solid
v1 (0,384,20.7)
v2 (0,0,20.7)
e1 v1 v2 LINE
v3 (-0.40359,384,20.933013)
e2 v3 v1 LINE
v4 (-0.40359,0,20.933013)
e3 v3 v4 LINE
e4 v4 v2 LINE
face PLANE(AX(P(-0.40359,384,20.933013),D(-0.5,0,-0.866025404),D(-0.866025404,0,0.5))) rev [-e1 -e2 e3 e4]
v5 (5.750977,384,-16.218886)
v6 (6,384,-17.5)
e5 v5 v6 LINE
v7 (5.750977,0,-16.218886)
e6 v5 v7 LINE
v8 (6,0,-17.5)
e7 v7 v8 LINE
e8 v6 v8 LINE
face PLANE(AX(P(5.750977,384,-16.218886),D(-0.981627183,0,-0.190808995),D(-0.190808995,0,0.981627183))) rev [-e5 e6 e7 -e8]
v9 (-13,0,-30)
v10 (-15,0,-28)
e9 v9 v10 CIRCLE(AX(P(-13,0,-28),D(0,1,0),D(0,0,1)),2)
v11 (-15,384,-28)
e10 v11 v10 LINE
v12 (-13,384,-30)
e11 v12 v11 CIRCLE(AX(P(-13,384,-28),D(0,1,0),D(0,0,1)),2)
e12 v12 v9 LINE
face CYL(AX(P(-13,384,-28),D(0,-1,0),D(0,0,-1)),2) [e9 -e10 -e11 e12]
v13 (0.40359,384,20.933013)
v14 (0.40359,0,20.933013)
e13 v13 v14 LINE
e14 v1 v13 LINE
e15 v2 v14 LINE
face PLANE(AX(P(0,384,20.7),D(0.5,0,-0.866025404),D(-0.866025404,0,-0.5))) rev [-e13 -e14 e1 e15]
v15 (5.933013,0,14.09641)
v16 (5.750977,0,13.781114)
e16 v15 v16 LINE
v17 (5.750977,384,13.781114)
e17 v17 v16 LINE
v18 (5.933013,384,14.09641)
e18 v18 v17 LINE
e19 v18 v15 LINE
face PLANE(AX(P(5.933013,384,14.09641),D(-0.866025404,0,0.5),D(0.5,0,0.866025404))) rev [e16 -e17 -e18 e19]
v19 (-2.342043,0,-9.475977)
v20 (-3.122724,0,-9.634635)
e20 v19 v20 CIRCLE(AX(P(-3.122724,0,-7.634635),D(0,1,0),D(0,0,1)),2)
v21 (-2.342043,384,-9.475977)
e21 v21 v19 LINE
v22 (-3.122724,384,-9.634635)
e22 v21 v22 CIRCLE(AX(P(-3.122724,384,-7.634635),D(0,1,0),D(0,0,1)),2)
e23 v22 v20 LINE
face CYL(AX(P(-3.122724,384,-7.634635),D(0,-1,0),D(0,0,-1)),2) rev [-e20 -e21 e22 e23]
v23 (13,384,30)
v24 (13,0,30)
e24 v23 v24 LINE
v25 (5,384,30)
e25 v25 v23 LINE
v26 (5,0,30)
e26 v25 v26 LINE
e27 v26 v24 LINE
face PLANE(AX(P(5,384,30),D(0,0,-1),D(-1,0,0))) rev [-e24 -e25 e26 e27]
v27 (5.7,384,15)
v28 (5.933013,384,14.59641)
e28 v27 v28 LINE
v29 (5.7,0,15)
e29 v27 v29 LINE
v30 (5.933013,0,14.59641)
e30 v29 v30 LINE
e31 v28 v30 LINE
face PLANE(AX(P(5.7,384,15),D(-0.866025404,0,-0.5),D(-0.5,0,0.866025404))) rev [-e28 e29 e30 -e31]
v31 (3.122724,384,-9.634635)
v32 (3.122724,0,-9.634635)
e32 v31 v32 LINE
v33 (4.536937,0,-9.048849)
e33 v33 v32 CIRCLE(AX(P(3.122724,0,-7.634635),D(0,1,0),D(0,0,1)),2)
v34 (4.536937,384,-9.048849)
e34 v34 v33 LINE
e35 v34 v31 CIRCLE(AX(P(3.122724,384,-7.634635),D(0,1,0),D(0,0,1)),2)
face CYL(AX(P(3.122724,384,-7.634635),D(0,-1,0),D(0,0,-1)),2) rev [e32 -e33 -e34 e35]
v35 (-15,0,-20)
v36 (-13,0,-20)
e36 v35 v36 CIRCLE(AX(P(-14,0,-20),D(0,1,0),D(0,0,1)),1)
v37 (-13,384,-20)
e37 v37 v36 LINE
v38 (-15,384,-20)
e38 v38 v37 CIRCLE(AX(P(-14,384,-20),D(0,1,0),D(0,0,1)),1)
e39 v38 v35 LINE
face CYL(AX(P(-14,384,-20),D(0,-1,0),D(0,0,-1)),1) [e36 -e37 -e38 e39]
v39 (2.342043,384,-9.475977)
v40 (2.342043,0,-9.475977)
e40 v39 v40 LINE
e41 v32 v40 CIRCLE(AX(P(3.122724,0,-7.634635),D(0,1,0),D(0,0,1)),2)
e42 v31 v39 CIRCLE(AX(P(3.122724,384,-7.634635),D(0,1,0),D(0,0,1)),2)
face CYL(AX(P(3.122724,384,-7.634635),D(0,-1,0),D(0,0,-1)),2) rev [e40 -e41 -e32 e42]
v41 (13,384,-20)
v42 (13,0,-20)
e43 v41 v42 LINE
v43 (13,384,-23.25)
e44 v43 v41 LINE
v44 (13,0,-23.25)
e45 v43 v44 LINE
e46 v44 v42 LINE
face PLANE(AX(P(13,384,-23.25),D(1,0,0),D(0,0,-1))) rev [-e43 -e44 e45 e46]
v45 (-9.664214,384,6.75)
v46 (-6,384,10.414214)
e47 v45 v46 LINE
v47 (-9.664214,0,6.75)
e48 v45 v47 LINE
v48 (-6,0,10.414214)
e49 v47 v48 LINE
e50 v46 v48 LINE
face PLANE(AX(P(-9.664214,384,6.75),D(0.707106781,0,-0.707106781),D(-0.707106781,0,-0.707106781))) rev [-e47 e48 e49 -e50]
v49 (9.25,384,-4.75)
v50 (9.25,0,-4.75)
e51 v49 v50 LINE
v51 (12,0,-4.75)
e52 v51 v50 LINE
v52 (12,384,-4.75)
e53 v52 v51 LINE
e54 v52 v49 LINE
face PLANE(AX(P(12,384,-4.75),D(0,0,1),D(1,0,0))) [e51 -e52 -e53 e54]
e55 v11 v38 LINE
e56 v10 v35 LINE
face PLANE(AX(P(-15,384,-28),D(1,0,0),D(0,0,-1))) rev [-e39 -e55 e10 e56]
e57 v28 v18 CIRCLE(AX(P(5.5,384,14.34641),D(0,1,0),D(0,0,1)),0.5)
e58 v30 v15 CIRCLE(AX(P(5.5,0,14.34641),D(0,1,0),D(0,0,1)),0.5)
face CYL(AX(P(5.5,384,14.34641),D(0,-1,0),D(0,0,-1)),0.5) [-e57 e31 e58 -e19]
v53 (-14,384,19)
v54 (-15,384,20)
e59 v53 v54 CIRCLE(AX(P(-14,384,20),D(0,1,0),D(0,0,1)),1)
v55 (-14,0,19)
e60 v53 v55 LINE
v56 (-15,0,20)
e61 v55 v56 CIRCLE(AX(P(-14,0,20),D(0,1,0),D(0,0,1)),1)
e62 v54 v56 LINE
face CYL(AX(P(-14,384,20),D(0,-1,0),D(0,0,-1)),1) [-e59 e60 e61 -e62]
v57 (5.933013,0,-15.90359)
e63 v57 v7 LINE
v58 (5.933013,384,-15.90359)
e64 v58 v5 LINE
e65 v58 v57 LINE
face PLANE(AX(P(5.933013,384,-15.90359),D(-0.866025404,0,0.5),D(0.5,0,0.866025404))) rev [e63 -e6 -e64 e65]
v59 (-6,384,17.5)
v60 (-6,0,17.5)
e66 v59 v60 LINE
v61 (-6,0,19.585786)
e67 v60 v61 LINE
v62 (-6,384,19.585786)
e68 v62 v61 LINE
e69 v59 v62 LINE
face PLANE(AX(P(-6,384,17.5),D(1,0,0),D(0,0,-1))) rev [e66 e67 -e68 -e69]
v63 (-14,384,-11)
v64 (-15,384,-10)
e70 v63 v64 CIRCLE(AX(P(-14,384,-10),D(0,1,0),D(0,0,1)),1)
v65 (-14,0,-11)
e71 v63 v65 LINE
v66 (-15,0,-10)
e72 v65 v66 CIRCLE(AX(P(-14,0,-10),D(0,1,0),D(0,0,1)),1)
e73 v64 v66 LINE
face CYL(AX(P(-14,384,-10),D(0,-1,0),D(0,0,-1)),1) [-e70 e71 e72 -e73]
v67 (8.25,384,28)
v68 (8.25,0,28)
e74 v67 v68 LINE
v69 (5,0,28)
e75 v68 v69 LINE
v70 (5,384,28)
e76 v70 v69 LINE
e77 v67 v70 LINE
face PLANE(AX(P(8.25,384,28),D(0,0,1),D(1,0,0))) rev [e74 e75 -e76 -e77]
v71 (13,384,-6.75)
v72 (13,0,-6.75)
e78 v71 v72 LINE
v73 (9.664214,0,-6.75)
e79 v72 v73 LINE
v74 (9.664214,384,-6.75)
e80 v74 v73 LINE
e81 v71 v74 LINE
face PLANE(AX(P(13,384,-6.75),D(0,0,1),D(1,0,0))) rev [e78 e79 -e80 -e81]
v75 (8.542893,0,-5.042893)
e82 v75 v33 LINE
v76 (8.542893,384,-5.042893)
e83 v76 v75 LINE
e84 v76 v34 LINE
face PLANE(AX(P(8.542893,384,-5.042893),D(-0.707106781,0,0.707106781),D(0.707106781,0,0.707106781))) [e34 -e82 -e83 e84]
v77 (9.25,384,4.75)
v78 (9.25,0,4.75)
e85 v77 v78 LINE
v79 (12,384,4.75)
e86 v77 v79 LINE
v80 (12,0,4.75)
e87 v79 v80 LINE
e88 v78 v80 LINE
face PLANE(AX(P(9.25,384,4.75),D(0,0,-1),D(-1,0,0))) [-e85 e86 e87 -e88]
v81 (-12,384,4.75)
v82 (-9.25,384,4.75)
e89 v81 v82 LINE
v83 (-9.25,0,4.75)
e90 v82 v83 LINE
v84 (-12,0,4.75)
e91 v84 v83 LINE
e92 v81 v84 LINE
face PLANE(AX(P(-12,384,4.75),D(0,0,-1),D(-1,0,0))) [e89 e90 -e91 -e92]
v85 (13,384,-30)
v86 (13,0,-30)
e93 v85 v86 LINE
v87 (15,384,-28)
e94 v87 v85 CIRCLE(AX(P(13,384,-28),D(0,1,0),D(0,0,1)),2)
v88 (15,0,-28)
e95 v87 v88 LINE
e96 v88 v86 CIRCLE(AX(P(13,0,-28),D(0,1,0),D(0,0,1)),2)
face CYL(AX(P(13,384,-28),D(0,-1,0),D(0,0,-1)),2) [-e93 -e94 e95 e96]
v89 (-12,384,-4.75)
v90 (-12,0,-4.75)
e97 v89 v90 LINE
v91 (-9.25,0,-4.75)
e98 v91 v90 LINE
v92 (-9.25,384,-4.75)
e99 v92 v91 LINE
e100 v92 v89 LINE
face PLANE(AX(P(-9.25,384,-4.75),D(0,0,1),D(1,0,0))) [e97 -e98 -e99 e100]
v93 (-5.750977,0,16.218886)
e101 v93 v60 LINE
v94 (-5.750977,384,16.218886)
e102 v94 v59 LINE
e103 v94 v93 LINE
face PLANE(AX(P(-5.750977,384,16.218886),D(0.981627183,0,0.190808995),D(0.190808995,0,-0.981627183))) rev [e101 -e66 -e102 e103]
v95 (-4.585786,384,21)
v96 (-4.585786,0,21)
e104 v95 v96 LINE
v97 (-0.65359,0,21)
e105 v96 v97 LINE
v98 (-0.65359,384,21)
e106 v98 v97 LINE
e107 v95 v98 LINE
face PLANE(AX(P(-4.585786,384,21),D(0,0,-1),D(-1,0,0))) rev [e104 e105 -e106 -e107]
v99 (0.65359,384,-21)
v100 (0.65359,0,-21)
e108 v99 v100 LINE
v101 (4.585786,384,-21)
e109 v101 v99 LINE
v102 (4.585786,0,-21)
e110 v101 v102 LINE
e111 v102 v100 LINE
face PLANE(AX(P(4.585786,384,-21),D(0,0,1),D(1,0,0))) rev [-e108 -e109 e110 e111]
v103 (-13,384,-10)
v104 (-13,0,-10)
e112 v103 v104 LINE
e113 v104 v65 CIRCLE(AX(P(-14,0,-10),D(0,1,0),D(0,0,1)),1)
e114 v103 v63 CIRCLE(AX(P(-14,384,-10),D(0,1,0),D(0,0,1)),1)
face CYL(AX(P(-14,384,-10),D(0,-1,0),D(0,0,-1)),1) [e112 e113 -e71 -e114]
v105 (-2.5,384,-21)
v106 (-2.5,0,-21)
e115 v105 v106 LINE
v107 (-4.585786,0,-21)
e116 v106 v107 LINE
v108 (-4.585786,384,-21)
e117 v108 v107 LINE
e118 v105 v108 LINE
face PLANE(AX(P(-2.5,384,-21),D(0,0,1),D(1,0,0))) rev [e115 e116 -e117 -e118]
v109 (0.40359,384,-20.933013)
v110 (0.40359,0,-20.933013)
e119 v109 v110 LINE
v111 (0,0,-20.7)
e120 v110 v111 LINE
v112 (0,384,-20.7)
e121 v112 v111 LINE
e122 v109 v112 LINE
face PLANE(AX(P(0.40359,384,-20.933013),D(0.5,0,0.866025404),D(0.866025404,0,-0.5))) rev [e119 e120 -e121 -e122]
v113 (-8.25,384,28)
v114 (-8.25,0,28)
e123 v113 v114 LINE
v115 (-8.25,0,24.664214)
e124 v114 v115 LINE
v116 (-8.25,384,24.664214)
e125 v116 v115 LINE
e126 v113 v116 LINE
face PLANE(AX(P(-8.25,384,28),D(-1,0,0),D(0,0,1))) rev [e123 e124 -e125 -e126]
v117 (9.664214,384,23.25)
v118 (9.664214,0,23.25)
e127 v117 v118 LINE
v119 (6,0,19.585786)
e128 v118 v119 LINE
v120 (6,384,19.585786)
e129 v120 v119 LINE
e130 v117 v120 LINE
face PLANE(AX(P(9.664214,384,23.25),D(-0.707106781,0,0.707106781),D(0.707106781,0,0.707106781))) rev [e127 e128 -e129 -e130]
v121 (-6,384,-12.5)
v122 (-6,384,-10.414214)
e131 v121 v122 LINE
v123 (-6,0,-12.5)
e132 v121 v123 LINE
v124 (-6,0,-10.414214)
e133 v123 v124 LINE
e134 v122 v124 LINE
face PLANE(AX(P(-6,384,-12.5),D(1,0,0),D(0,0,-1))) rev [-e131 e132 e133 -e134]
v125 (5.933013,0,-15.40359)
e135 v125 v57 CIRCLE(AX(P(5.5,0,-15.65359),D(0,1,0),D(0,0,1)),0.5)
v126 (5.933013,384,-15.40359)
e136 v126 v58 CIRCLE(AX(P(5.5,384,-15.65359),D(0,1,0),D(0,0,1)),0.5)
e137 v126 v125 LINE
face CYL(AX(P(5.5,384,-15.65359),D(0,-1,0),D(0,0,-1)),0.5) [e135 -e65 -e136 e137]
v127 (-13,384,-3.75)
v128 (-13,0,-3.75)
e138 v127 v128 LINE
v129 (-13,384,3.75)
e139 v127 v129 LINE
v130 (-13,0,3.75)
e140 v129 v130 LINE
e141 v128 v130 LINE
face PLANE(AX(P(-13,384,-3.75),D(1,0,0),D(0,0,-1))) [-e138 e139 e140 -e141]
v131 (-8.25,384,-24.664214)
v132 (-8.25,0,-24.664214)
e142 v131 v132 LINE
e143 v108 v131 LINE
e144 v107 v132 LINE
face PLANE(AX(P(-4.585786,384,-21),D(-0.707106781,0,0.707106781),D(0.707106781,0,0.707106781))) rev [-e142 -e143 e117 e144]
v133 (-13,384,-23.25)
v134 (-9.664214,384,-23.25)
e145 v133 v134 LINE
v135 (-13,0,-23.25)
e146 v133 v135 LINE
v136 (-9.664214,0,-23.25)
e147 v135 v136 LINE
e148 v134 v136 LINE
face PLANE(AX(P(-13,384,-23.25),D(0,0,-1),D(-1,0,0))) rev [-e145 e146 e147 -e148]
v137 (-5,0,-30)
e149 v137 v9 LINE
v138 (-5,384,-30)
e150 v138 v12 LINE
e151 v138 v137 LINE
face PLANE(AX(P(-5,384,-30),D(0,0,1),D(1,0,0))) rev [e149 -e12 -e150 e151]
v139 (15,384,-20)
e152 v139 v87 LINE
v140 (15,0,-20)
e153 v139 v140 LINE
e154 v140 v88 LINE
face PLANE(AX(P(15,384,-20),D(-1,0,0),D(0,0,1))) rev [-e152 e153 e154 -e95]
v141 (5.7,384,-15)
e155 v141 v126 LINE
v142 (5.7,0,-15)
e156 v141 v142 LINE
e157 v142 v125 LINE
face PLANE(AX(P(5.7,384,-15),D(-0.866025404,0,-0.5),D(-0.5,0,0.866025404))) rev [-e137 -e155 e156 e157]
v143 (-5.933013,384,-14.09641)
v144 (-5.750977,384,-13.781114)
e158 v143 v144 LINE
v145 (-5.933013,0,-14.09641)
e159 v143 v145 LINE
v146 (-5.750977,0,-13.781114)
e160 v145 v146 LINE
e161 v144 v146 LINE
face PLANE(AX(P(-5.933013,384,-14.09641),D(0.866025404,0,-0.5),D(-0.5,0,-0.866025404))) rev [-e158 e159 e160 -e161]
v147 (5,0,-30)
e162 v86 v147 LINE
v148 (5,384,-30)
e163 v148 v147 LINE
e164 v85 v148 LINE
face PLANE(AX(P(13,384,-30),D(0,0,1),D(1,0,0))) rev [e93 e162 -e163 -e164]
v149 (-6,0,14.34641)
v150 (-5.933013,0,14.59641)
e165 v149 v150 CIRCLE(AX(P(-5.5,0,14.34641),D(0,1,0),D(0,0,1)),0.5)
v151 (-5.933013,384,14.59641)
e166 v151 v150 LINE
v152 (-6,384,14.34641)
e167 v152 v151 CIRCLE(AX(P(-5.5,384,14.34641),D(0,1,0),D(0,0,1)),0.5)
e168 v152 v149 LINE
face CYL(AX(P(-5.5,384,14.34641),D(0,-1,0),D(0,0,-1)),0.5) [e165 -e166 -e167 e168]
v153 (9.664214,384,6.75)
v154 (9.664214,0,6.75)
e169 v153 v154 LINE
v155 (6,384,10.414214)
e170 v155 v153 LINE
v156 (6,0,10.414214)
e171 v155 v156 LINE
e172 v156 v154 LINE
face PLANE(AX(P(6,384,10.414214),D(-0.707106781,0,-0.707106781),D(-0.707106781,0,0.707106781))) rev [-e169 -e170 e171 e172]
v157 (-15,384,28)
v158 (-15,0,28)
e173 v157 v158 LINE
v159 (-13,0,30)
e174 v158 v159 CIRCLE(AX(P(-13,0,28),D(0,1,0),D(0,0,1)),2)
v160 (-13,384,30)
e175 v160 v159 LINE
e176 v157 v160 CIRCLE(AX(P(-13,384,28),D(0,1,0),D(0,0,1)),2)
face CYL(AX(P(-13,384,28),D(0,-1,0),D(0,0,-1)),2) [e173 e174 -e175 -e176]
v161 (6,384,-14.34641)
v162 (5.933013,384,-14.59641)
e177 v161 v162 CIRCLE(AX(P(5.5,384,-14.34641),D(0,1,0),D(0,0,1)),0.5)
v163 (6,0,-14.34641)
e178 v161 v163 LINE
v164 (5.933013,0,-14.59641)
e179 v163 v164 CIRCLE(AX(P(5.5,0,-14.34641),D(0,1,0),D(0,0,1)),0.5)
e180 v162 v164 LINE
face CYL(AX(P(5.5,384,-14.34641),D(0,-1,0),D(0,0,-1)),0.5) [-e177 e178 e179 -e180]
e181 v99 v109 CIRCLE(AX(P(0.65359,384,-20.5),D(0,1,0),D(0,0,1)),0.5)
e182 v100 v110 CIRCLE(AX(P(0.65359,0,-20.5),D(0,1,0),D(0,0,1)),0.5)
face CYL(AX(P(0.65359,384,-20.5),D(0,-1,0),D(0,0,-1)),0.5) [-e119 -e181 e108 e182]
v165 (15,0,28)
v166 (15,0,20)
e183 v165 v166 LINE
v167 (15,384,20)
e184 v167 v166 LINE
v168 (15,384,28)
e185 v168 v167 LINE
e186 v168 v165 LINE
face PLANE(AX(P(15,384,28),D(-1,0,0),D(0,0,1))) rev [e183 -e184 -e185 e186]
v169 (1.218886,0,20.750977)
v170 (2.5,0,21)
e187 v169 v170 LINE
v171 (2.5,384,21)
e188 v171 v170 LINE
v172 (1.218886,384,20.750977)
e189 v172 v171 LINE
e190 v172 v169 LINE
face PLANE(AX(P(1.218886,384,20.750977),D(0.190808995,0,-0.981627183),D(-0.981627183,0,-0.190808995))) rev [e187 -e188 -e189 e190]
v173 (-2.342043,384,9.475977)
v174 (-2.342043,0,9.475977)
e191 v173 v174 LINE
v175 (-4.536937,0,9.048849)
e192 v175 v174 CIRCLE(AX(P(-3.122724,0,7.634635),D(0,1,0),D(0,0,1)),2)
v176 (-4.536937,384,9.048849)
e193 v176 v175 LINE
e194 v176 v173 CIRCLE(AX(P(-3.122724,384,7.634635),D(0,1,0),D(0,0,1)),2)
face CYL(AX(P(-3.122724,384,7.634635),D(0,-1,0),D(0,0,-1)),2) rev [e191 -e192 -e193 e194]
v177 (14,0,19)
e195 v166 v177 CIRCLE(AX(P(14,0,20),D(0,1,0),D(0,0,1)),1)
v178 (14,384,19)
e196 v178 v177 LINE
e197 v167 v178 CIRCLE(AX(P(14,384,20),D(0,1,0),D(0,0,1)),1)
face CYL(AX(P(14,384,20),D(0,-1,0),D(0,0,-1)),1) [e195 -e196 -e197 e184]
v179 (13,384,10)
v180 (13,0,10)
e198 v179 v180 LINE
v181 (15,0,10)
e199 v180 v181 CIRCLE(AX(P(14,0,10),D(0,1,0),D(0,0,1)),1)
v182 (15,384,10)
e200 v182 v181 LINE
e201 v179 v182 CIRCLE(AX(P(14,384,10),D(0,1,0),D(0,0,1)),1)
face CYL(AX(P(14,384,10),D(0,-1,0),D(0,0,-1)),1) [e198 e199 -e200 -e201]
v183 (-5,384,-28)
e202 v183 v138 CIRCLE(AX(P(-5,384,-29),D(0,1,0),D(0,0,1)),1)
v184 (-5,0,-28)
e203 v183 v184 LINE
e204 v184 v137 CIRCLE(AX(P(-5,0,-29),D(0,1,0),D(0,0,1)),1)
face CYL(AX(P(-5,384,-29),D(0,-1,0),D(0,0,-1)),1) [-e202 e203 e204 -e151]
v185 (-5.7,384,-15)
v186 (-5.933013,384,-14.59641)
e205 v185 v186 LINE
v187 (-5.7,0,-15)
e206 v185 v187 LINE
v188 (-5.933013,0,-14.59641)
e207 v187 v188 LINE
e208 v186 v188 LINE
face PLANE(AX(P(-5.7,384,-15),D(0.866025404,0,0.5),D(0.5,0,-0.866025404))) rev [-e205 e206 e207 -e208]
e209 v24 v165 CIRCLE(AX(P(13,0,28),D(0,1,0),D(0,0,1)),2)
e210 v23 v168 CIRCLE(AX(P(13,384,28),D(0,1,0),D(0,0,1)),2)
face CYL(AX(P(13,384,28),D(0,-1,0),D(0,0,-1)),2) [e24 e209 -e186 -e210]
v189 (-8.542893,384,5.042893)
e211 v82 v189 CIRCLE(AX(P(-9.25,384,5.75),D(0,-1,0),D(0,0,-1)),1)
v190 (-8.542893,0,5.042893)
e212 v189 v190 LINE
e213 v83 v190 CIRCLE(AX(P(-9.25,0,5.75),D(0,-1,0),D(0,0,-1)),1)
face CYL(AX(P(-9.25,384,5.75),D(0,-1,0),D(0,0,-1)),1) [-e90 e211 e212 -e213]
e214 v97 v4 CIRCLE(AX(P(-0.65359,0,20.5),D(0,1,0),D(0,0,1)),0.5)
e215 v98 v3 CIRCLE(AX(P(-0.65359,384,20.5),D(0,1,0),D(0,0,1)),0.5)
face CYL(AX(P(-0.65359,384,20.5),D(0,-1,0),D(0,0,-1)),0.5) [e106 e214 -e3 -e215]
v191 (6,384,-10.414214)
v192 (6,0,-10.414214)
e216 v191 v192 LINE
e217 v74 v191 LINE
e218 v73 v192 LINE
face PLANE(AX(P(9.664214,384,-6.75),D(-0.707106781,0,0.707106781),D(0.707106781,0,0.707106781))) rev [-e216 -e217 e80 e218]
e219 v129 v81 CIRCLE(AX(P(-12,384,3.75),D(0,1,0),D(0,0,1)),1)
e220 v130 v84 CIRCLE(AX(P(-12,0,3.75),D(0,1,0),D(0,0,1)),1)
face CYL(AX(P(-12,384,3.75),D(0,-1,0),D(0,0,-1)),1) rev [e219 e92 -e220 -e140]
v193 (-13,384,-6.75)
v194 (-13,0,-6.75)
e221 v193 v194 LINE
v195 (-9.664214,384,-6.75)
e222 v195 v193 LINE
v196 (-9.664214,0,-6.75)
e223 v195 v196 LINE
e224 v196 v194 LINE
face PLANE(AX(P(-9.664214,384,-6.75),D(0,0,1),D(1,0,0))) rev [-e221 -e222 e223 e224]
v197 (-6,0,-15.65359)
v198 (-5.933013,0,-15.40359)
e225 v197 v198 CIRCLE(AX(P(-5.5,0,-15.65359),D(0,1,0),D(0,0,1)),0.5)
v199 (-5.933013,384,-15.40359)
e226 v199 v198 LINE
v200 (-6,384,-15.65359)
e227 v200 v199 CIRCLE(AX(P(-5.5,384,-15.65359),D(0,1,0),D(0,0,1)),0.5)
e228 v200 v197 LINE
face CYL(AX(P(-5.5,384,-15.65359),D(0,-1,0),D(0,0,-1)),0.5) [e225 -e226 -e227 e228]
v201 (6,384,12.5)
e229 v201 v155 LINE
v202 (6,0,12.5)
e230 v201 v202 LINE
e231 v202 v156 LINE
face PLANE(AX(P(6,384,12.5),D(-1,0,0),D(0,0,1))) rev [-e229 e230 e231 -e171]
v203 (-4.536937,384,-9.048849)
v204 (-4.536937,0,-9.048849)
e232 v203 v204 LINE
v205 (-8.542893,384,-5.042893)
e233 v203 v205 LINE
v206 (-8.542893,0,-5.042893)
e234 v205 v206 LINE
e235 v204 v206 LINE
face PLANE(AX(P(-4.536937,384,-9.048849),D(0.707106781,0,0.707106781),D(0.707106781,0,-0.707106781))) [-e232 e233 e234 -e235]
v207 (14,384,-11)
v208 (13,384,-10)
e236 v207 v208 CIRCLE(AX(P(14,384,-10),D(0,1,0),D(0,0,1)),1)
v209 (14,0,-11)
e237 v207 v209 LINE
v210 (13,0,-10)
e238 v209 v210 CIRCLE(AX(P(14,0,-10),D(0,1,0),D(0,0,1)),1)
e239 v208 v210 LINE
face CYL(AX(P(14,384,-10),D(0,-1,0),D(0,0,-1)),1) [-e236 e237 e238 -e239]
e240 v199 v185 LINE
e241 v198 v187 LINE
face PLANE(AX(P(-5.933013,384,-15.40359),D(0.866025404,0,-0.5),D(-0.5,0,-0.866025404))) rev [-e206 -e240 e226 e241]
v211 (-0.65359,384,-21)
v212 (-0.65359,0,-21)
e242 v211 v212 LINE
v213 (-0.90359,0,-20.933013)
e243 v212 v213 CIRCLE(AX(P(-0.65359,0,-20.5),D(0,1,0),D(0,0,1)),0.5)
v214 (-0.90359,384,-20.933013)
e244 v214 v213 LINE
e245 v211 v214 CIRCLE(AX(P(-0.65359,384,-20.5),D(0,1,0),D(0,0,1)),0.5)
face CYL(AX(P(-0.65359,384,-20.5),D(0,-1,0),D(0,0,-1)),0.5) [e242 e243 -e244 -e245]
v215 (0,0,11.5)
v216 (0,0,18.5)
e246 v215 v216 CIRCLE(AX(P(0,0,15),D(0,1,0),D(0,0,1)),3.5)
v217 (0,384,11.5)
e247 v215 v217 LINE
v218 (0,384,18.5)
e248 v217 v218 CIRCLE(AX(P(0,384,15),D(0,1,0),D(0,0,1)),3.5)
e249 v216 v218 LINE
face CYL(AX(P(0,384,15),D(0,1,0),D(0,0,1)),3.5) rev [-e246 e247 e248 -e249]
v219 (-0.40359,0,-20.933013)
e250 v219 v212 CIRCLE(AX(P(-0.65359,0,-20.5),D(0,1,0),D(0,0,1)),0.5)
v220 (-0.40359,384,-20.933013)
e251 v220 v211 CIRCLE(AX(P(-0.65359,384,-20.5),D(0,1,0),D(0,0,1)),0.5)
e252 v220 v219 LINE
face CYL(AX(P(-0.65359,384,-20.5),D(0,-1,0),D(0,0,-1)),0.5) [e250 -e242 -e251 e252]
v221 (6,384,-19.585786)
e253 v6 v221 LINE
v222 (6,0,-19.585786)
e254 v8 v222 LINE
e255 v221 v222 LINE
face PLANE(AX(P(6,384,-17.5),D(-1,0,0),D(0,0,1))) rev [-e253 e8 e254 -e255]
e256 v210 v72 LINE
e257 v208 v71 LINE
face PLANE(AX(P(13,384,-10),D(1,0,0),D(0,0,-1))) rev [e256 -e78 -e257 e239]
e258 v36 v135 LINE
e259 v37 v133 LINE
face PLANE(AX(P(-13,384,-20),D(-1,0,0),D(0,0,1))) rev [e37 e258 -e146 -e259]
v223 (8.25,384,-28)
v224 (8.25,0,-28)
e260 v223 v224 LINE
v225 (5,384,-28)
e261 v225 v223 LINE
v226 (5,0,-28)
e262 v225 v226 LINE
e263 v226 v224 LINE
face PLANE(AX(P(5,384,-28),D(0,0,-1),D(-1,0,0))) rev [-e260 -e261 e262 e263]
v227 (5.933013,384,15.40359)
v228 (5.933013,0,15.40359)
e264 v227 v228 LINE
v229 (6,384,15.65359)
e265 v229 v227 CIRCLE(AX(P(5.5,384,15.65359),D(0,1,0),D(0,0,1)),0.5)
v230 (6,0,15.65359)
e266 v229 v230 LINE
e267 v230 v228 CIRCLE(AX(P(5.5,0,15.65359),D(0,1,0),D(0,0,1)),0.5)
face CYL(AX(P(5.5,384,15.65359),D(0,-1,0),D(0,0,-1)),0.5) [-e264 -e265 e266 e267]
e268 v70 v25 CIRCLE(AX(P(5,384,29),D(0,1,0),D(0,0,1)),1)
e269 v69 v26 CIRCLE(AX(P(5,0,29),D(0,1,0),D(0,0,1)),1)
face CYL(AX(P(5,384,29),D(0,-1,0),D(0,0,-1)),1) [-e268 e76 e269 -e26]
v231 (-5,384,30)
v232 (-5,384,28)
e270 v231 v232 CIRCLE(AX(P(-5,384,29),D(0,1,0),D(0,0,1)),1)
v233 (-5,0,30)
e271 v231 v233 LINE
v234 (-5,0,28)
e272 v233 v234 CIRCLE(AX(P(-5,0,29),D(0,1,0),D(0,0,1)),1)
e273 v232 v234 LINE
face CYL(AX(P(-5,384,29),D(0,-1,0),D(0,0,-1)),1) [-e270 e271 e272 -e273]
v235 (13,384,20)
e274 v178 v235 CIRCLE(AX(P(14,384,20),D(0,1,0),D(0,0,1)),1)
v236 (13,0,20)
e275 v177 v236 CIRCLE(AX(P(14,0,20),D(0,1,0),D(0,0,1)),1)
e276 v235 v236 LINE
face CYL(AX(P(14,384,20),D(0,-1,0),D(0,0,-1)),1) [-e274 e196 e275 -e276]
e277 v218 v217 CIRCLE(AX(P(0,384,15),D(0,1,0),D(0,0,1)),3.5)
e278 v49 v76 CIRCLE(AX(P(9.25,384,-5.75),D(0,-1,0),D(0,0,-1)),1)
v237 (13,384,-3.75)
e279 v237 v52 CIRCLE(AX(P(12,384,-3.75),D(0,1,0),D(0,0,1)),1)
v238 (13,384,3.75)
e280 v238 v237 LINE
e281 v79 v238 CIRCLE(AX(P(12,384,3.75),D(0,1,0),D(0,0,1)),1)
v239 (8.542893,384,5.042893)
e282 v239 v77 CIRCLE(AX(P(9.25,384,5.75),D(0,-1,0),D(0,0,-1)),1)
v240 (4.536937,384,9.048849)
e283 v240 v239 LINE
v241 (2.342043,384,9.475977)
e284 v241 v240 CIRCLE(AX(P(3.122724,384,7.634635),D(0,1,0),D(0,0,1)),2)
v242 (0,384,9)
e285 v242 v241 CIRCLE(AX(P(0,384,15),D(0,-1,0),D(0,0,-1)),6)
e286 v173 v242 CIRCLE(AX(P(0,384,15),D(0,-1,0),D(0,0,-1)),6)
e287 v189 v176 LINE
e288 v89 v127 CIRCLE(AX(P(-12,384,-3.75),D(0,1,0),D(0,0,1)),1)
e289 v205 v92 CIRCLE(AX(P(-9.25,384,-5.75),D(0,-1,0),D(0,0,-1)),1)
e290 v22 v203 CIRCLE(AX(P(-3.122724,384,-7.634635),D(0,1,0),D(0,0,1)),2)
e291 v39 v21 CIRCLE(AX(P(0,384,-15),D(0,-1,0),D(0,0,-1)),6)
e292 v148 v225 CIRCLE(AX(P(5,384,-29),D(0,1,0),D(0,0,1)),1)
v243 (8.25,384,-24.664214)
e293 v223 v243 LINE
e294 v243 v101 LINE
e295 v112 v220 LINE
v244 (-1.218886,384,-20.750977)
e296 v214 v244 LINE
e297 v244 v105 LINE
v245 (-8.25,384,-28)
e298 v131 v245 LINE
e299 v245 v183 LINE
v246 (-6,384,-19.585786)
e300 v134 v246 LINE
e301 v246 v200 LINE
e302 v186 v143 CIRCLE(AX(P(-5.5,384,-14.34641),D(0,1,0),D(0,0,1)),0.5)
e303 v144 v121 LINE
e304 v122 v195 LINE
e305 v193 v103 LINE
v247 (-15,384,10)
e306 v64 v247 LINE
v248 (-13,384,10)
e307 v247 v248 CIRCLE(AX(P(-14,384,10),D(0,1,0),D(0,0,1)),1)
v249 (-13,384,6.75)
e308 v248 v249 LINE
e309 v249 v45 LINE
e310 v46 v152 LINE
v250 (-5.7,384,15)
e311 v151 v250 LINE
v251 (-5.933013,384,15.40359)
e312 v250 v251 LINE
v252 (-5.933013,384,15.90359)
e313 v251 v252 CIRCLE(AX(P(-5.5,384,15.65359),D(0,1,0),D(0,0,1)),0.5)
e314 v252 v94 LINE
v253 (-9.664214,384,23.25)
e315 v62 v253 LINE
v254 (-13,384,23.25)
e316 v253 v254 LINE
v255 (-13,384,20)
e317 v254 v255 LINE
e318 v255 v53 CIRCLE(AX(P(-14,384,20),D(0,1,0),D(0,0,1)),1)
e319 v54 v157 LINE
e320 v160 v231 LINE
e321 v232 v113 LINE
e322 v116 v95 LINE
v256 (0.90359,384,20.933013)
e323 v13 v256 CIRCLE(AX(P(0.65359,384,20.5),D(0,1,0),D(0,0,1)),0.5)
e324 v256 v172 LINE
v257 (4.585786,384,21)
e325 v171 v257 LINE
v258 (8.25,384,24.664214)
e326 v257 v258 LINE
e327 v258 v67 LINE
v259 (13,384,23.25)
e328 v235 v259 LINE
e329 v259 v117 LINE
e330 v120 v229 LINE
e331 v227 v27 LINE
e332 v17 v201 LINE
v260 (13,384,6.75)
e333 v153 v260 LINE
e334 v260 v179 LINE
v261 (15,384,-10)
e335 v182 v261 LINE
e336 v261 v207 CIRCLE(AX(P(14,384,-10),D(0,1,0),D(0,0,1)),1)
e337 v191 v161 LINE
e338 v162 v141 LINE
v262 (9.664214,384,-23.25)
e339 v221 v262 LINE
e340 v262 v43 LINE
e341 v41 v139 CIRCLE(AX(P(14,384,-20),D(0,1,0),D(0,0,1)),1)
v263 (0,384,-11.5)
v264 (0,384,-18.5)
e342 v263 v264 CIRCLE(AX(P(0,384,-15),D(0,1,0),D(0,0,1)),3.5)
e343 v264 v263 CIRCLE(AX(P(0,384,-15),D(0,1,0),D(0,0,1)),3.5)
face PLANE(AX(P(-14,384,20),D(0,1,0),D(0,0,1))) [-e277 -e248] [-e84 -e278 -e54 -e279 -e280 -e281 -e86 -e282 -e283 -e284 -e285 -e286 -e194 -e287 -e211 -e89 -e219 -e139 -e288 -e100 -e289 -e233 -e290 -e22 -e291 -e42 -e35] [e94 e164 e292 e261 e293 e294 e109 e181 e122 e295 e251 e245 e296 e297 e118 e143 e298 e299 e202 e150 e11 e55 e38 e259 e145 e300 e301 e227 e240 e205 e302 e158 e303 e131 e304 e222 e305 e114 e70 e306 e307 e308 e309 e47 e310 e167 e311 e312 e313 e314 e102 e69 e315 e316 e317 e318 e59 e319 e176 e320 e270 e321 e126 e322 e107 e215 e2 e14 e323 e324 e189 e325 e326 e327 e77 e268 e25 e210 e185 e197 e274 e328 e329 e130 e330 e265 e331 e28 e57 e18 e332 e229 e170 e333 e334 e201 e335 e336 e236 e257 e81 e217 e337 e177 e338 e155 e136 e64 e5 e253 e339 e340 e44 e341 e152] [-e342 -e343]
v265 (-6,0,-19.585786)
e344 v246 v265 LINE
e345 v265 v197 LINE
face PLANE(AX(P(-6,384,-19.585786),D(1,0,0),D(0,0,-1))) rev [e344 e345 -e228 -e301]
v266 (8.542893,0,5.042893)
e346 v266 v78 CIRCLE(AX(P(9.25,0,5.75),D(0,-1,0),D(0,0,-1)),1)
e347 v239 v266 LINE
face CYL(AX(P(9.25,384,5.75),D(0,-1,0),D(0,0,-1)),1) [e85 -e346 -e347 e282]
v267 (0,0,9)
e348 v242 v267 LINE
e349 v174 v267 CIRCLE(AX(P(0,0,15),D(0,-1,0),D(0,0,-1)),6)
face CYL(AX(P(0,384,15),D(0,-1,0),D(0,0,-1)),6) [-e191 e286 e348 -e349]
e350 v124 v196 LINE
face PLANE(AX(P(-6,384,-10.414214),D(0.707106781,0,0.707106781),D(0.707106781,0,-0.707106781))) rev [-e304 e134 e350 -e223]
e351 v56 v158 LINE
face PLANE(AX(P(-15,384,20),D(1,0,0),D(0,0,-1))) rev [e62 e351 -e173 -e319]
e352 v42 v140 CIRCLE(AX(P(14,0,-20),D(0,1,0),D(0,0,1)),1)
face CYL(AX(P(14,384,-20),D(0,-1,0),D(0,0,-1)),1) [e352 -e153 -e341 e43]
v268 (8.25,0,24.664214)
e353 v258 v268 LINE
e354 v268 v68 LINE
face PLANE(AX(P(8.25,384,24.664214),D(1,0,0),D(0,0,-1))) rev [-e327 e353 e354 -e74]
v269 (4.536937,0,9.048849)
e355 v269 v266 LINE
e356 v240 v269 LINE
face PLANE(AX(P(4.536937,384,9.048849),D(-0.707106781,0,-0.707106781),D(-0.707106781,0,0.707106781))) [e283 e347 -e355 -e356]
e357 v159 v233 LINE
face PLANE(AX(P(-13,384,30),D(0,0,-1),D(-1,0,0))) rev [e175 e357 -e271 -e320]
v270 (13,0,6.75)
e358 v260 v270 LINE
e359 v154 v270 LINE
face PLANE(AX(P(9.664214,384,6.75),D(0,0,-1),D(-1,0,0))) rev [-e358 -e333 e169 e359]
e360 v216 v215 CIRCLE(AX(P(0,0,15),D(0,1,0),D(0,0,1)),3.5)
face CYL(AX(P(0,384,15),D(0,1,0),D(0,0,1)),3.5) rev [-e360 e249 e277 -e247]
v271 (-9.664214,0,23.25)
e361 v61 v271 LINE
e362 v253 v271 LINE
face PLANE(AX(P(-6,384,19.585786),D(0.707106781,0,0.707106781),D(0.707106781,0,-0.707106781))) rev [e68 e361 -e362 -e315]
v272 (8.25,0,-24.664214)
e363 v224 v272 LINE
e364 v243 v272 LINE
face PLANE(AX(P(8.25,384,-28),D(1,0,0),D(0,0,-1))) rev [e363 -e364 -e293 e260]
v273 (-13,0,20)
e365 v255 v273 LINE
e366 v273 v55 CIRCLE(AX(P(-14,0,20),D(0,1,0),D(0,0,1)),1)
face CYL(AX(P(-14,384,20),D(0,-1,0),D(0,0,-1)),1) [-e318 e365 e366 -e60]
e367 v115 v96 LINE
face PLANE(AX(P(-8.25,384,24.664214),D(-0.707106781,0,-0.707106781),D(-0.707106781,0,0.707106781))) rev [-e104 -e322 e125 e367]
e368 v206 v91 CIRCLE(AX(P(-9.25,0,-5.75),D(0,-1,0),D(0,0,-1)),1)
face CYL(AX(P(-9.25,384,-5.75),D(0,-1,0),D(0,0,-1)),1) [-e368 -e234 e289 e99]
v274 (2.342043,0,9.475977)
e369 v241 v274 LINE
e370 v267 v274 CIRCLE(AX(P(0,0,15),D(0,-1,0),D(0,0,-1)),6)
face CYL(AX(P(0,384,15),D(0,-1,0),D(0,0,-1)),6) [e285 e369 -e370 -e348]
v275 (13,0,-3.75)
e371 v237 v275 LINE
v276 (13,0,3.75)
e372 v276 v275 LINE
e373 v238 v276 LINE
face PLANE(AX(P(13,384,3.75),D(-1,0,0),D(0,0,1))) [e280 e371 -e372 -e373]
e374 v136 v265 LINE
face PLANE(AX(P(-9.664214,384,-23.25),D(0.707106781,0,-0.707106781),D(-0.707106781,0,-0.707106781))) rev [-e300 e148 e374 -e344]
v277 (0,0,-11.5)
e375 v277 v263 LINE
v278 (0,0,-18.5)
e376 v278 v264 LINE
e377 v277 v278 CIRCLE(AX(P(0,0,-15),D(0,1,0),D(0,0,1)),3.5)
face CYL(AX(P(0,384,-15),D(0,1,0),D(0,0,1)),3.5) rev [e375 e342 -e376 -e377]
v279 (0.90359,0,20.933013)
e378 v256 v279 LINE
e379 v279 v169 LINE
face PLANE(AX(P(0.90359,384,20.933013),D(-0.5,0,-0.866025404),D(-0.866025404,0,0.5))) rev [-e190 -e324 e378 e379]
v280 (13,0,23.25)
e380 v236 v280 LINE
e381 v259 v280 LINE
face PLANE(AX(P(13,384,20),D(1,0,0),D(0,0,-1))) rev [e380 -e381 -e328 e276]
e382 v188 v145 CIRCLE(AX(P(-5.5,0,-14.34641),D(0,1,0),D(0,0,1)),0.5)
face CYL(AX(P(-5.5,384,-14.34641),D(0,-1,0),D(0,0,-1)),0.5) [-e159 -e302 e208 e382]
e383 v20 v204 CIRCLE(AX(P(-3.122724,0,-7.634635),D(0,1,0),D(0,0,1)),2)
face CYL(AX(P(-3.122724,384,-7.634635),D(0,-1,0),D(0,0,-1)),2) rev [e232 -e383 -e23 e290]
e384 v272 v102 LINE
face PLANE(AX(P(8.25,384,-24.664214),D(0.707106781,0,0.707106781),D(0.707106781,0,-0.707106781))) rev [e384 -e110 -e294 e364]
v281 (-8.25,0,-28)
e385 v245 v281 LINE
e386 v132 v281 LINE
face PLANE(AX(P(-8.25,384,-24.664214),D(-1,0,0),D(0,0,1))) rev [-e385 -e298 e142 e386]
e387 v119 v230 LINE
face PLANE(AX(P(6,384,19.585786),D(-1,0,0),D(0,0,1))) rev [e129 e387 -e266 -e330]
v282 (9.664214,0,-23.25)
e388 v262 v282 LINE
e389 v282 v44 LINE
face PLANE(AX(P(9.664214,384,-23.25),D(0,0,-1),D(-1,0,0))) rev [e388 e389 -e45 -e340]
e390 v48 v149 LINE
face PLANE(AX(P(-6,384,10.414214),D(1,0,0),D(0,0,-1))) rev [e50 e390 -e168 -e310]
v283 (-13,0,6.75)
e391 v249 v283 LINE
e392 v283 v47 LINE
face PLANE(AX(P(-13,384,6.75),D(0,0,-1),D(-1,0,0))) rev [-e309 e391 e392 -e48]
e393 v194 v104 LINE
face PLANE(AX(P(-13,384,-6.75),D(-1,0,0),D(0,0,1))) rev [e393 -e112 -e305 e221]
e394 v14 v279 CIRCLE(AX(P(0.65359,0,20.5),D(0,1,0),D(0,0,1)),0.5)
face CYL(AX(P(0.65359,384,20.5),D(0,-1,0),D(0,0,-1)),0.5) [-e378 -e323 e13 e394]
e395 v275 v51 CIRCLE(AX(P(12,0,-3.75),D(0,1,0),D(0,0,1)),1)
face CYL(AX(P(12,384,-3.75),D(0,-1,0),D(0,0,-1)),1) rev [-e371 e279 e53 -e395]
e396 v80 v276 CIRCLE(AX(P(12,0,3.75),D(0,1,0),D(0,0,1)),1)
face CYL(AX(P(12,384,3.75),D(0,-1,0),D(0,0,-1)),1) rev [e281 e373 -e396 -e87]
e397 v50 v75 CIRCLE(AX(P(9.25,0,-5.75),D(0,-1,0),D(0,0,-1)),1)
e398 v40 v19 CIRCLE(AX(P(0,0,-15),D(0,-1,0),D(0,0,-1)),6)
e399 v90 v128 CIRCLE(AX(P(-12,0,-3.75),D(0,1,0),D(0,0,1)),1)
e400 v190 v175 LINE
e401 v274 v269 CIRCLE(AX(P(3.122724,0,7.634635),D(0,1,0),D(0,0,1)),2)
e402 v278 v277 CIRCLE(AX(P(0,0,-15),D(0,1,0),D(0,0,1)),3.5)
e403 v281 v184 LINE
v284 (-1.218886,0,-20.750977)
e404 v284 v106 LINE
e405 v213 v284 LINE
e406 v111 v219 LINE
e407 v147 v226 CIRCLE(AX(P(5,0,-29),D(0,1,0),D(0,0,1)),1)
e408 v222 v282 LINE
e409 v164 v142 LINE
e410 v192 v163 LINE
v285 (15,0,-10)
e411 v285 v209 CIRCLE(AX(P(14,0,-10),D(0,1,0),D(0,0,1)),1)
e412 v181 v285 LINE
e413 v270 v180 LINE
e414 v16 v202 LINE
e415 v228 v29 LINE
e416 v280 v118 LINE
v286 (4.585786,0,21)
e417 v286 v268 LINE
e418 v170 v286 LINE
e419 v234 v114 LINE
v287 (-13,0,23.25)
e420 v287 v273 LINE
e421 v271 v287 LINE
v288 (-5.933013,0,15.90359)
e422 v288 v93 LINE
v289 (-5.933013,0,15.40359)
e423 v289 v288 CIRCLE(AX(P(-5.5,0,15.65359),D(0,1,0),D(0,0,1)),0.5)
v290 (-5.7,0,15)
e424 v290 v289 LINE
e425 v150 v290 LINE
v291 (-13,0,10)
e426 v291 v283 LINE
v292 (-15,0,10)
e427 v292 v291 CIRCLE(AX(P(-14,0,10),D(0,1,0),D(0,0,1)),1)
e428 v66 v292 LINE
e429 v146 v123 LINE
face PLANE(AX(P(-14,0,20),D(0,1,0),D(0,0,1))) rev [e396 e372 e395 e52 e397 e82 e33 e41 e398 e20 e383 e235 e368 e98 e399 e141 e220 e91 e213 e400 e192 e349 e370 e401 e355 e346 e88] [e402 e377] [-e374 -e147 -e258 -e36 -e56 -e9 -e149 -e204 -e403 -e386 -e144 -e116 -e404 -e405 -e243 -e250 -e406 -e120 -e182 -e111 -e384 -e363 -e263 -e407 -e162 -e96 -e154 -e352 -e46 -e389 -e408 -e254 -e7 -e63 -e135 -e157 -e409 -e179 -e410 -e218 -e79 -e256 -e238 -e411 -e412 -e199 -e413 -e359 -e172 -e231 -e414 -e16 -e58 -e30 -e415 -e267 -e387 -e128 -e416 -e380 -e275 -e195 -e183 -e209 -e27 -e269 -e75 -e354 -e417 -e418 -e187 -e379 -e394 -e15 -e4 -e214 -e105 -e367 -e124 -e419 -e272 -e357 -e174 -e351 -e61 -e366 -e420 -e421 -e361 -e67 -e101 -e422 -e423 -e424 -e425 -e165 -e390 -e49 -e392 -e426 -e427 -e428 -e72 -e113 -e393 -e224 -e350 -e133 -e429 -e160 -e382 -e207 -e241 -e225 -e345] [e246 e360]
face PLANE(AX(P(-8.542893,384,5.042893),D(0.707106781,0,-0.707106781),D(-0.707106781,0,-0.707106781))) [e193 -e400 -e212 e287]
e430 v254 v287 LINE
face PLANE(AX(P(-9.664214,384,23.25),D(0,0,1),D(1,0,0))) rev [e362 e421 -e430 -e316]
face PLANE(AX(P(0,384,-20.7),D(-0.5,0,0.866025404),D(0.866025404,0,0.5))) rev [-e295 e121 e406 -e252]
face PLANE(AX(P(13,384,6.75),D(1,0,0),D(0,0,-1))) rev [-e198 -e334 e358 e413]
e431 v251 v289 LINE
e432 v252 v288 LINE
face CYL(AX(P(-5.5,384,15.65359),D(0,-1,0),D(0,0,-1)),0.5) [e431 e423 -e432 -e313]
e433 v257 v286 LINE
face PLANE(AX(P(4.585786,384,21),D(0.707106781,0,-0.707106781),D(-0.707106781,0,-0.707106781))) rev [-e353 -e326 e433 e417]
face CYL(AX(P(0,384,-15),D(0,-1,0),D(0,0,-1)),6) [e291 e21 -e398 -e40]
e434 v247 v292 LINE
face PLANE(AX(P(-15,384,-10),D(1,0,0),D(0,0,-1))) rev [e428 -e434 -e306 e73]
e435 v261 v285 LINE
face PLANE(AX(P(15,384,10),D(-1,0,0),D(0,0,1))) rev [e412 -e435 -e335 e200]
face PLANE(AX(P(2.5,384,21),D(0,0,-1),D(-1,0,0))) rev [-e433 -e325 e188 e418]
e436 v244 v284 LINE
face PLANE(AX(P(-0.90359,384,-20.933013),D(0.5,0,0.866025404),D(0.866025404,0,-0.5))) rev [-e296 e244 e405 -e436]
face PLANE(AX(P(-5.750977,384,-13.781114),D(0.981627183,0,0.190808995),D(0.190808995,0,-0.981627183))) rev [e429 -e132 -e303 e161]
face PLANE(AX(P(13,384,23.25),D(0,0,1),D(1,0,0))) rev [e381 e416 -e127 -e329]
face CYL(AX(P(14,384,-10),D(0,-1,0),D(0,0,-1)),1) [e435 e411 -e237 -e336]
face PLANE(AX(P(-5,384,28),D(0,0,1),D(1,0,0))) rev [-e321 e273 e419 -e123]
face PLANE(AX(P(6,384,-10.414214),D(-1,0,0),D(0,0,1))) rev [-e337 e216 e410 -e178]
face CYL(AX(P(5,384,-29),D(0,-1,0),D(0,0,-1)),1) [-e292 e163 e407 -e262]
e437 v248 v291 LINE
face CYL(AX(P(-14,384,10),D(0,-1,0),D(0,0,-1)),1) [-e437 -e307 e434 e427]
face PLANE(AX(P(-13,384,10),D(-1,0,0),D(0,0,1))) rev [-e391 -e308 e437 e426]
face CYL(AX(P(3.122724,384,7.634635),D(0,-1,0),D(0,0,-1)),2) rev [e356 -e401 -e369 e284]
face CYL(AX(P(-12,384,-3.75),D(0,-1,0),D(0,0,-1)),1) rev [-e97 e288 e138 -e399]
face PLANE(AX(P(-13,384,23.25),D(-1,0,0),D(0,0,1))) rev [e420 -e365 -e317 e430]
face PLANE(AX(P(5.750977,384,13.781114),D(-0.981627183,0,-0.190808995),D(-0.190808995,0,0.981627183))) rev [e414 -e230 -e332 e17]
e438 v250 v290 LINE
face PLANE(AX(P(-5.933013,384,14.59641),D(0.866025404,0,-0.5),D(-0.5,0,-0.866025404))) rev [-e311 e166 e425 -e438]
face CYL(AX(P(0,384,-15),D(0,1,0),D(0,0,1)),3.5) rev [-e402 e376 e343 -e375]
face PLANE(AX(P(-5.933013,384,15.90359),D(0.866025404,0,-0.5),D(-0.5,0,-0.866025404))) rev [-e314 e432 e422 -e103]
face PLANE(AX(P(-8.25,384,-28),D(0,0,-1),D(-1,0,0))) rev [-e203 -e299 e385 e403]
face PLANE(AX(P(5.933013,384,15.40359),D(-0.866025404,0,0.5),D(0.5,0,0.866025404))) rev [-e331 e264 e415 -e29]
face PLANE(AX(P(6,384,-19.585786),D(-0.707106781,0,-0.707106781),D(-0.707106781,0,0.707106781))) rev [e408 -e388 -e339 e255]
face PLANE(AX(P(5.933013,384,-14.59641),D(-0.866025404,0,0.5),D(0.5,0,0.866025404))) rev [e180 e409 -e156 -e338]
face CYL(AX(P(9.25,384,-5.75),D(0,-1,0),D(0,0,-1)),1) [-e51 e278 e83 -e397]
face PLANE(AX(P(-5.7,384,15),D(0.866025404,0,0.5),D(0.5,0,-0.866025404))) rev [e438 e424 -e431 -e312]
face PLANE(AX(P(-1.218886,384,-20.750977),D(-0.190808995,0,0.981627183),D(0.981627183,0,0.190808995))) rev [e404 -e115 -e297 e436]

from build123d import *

# Parameters (mm, degrees)
SKETCH11_R                             = 3.4
ALUMINIUM_PROFILE_30_X_60_X_R2_1_DEPTH = 384
M8X1_0_TAPPED_HOLE1_D                  = 7
M8X1_0_TAPPED_HOLE1_DEPTH              = 389
M8X1_0_TAPPED_HOLE1_TIP                = 2.103012167
M8X1_0_TAPPED_HOLE2_D                  = 7
M8X1_0_TAPPED_HOLE2_DEPTH              = 15
M8X1_0_TAPPED_HOLE2_TIP                = 2.103012167


with BuildPart() as part:
    # Sketch11 → Aluminium profile 30 X 60 X R2(1) (new body)
    with BuildSketch(Plane(origin=(0, 0, 0), x_dir=(1, 0, 0), z_dir=(0, 1, 0))):
        with BuildLine():
            Line((-15, -20), (-15, -28))
            ThreePointArc((-15, -28), (-14.414213562, -29.414213562), (-13, -30))
            Line((-13, -30), (-5, -30))
            ThreePointArc((-5, -30), (-4, -29), (-5, -28))
            Line((-5, -28), (-8.25, -28))
            Line((-8.25, -28), (-8.25, -24.664213562))
            Line((-8.25, -24.664213562), (-4.585786438, -21))
            Line((-4.585786438, -21), (-0.653589838, -21))
            ThreePointArc((-0.653589838, -21), (-0.524180316, -20.982962913), (-0.403589838, -20.933012702))
            Line((-0.403589838, -20.933012702), (0, -20.7))
            Line((0, -20.7), (0.403589838, -20.933012702))
            ThreePointArc((0.403589838, -20.933012702), (0.653589838, -21), (0.903589838, -20.933012702))
            Line((0.903589838, -20.933012702), (1.218885629, -20.750976592))
            Line((1.218885629, -20.750976592), (2.5, -21))
            Line((2.5, -21), (4.585786438, -21))
            Line((4.585786438, -21), (8.25, -24.664213562))
            Line((8.25, -24.664213562), (8.25, -28))
            Line((8.25, -28), (5, -28))
            ThreePointArc((5, -28), (4, -29), (5, -30))
            Line((5, -30), (13, -30))
            ThreePointArc((13, -30), (14.414213562, -29.414213562), (15, -28))
            Line((15, -28), (15, -20.00000006))
            ThreePointArc((15, -20.00000006), (14, -19.00000006), (13, -20.00000006))
            Line((13, -20.00000006), (13, -23.25))
            Line((13, -23.25), (9.664213562, -23.25))
            Line((9.664213562, -23.25), (6, -19.585786438))
            Line((6, -19.585786438), (6, -15.653589838))
            ThreePointArc((6, -15.653589838), (5.982962913, -15.524180316), (5.933012702, -15.403589838))
            Line((5.933012702, -15.403589838), (5.7, -15))
            Line((5.7, -15), (5.933012702, -14.596410162))
            ThreePointArc((5.933012702, -14.596410162), (6, -14.346410162), (5.933012702, -14.096410162))
            Line((5.933012702, -14.096410162), (5.750976592, -13.781114371))
            Line((5.750976592, -13.781114371), (6, -12.5))
            Line((6, -12.5), (6, -10.414213562))
            Line((6, -10.414213562), (9.664213562, -6.75))
            Line((9.664213562, -6.75), (13, -6.75))
            Line((13, -6.75), (13, -9.999999769))
            ThreePointArc((13, -9.999999769), (14, -10.999999769), (15, -9.999999769))
            Line((15, -9.999999769), (15, 9.99999994))
            ThreePointArc((15, 9.99999994), (14, 10.99999994), (13, 9.99999994))
            Line((13, 9.99999994), (13, 6.75))
            Line((13, 6.75), (9.664213562, 6.75))
            Line((9.664213562, 6.75), (6, 10.414213562))
            Line((6, 10.414213562), (6, 14.346410162))
            ThreePointArc((6, 14.346410162), (5.982962913, 14.475819684), (5.933012702, 14.596410162))
            Line((5.933012702, 14.596410162), (5.7, 15))
            Line((5.7, 15), (5.933012702, 15.403589838))
            ThreePointArc((5.933012702, 15.403589838), (6, 15.653589838), (5.933012702, 15.903589838))
            Line((5.933012702, 15.903589838), (5.750976592, 16.218885629))
            Line((5.750976592, 16.218885629), (6, 17.5))
            Line((6, 17.5), (6, 19.585786438))
            Line((6, 19.585786438), (9.664213562, 23.25))
            Line((9.664213562, 23.25), (13, 23.25))
            Line((13, 23.25), (13, 20))
            ThreePointArc((13, 20), (14, 19), (15, 20))
            Line((15, 20), (15, 28))
            ThreePointArc((15, 28), (14.414213562, 29.414213562), (13, 30))
            Line((13, 30), (5, 30))
            ThreePointArc((5, 30), (4, 29), (5, 28))
            Line((5, 28), (8.25, 28))
            Line((8.25, 28), (8.25, 24.664213562))
            Line((8.25, 24.664213562), (4.585786438, 21))
            Line((4.585786438, 21), (0.653589838, 21))
            ThreePointArc((0.653589838, 21), (0.524180316, 20.982962913), (0.403589838, 20.933012702))
            Line((0.403589838, 20.933012702), (0, 20.7))
            Line((0, 20.7), (-0.403589838, 20.933012702))
            ThreePointArc((-0.403589838, 20.933012702), (-0.653589838, 21), (-0.903589838, 20.933012702))
            Line((-0.903589838, 20.933012702), (-1.218885629, 20.750976592))
            Line((-1.218885629, 20.750976592), (-2.5, 21))
            Line((-2.5, 21), (-4.585786438, 21))
            Line((-4.585786438, 21), (-8.25, 24.664213562))
            Line((-8.25, 24.664213562), (-8.25, 28))
            Line((-8.25, 28), (-5, 28))
            ThreePointArc((-5, 28), (-4, 29), (-5, 30))
            Line((-5, 30), (-13, 30))
            ThreePointArc((-13, 30), (-14.414213562, 29.414213562), (-15, 28))
            Line((-15, 28), (-15, 20))
            ThreePointArc((-15, 20), (-14, 19), (-13, 20))
            Line((-13, 20), (-13, 23.25))
            Line((-13, 23.25), (-9.664213562, 23.25))
            Line((-9.664213562, 23.25), (-6, 19.585786438))
            Line((-6, 19.585786438), (-6, 15.653589838))
            ThreePointArc((-6, 15.653589838), (-5.982962913, 15.524180316), (-5.933012702, 15.403589838))
            Line((-5.933012702, 15.403589838), (-5.7, 15))
            Line((-5.7, 15), (-5.933012702, 14.596410162))
            ThreePointArc((-5.933012702, 14.596410162), (-6, 14.346410162), (-5.933012702, 14.096410162))
            Line((-5.933012702, 14.096410162), (-5.750976592, 13.781114371))
            Line((-5.750976592, 13.781114371), (-6, 12.5))
            Line((-6, 12.5), (-6, 10.414213562))
            Line((-6, 10.414213562), (-9.664213562, 6.75))
            Line((-9.664213562, 6.75), (-13, 6.75))
            Line((-13, 6.75), (-13, 9.99999994))
            ThreePointArc((-13, 9.99999994), (-14, 10.99999994), (-15, 9.99999994))
            Line((-15, 9.99999994), (-15, -9.999999769))
            ThreePointArc((-15, -9.999999769), (-14, -10.999999769), (-13, -9.999999769))
            Line((-13, -9.999999769), (-13, -6.75))
            Line((-13, -6.75), (-9.664213562, -6.75))
            Line((-9.664213562, -6.75), (-6, -10.414213562))
            Line((-6, -10.414213562), (-6, -14.346410162))
            ThreePointArc((-6, -14.346410162), (-5.982962913, -14.475819684), (-5.933012702, -14.596410162))
            Line((-5.933012702, -14.596410162), (-5.7, -15))
            Line((-5.7, -15), (-5.933012702, -15.403589838))
            ThreePointArc((-5.933012702, -15.403589838), (-6, -15.653589838), (-5.933012702, -15.903589838))
            Line((-5.933012702, -15.903589838), (-5.750976592, -16.218885629))
            Line((-5.750976592, -16.218885629), (-6, -17.5))
            Line((-6, -17.5), (-6, -19.585786438))
            Line((-6, -19.585786438), (-9.664213562, -23.25))
            Line((-9.664213562, -23.25), (-13, -23.25))
            Line((-13, -23.25), (-13, -20))
            ThreePointArc((-13, -20), (-14, -19), (-15, -20))
        make_face()
        with Locations((0, 15)):
            Circle(SKETCH11_R, mode=Mode.SUBTRACT)
        with Locations((0, -15)):
            Circle(SKETCH11_R, mode=Mode.SUBTRACT)
        with BuildLine():
            Line((-13, 3.75), (-13, -3.75))
            ThreePointArc((-13, -3.75), (-12.707106781, -4.457106781), (-12, -4.75))
            Line((-12, -4.75), (-9.25, -4.75))
            ThreePointArc((-9.25, -4.75), (-8.867316568, -4.826120467), (-8.542893219, -5.042893219))
            Line((-8.542893219, -5.042893219), (-4.53693746, -9.048848978))
            ThreePointArc((-4.53693746, -9.048848978), (-3.504758422, -9.597808771), (-2.342042923, -9.475976562))
            ThreePointArc((-2.342042923, -9.475976562), (0, -9), (2.342042923, -9.475976562))
            ThreePointArc((2.342042923, -9.475976562), (3.504758422, -9.597808771), (4.53693746, -9.048848978))
            Line((4.53693746, -9.048848978), (8.542893219, -5.042893219))
            ThreePointArc((8.542893219, -5.042893219), (8.867316568, -4.826120467), (9.25, -4.75))
            Line((9.25, -4.75), (12, -4.75))
            ThreePointArc((12, -4.75), (12.707106781, -4.457106781), (13, -3.75))
            Line((13, -3.75), (13, 3.75))
            ThreePointArc((13, 3.75), (12.707106781, 4.457106781), (12, 4.75))
            Line((12, 4.75), (9.25, 4.75))
            ThreePointArc((9.25, 4.75), (8.867316568, 4.826120467), (8.542893219, 5.042893219))
            Line((8.542893219, 5.042893219), (4.53693746, 9.048848978))
            ThreePointArc((4.53693746, 9.048848978), (3.504758422, 9.597808771), (2.342042923, 9.475976562))
            ThreePointArc((2.342042923, 9.475976562), (0, 9), (-2.342042923, 9.475976562))
            ThreePointArc((-2.342042923, 9.475976562), (-3.504758422, 9.597808771), (-4.53693746, 9.048848978))
            Line((-4.53693746, 9.048848978), (-8.542893219, 5.042893219))
            ThreePointArc((-8.542893219, 5.042893219), (-8.867316568, 4.826120467), (-9.25, 4.75))
            Line((-9.25, 4.75), (-12, 4.75))
            ThreePointArc((-12, 4.75), (-12.707106781, 4.457106781), (-13, 3.75))
        make_face(mode=Mode.SUBTRACT)
    extrude(amount=ALUMINIUM_PROFILE_30_X_60_X_R2_1_DEPTH)

    # M8x1.0 Tapped Hole1
    with Locations(Plane(origin=(0, 384, 0), x_dir=(1, 0, 0), z_dir=(0, 1, 0))):
        with Locations((0, 15), (0, -15)):
            Hole(M8X1_0_TAPPED_HOLE1_D / 2, depth=M8X1_0_TAPPED_HOLE1_DEPTH)
            with Locations((0, 0, -(M8X1_0_TAPPED_HOLE1_DEPTH + M8X1_0_TAPPED_HOLE1_TIP / 2))):  # 118° drill point
                Cone(0, M8X1_0_TAPPED_HOLE1_D / 2, M8X1_0_TAPPED_HOLE1_TIP, mode=Mode.SUBTRACT)

    # M8x1.0 Tapped Hole2
    with Locations(Plane(origin=(0, 0, -15), x_dir=(0, 0, -1), z_dir=(0, -1, 0))):
        with Locations((0, 0), (-30, 0)):
            Hole(M8X1_0_TAPPED_HOLE2_D / 2, depth=M8X1_0_TAPPED_HOLE2_DEPTH)
            with Locations((0, 0, -(M8X1_0_TAPPED_HOLE2_DEPTH + M8X1_0_TAPPED_HOLE2_TIP / 2))):  # 118° drill point
                Cone(0, M8X1_0_TAPPED_HOLE2_D / 2, M8X1_0_TAPPED_HOLE2_TIP, mode=Mode.SUBTRACT)


solid = part.part
